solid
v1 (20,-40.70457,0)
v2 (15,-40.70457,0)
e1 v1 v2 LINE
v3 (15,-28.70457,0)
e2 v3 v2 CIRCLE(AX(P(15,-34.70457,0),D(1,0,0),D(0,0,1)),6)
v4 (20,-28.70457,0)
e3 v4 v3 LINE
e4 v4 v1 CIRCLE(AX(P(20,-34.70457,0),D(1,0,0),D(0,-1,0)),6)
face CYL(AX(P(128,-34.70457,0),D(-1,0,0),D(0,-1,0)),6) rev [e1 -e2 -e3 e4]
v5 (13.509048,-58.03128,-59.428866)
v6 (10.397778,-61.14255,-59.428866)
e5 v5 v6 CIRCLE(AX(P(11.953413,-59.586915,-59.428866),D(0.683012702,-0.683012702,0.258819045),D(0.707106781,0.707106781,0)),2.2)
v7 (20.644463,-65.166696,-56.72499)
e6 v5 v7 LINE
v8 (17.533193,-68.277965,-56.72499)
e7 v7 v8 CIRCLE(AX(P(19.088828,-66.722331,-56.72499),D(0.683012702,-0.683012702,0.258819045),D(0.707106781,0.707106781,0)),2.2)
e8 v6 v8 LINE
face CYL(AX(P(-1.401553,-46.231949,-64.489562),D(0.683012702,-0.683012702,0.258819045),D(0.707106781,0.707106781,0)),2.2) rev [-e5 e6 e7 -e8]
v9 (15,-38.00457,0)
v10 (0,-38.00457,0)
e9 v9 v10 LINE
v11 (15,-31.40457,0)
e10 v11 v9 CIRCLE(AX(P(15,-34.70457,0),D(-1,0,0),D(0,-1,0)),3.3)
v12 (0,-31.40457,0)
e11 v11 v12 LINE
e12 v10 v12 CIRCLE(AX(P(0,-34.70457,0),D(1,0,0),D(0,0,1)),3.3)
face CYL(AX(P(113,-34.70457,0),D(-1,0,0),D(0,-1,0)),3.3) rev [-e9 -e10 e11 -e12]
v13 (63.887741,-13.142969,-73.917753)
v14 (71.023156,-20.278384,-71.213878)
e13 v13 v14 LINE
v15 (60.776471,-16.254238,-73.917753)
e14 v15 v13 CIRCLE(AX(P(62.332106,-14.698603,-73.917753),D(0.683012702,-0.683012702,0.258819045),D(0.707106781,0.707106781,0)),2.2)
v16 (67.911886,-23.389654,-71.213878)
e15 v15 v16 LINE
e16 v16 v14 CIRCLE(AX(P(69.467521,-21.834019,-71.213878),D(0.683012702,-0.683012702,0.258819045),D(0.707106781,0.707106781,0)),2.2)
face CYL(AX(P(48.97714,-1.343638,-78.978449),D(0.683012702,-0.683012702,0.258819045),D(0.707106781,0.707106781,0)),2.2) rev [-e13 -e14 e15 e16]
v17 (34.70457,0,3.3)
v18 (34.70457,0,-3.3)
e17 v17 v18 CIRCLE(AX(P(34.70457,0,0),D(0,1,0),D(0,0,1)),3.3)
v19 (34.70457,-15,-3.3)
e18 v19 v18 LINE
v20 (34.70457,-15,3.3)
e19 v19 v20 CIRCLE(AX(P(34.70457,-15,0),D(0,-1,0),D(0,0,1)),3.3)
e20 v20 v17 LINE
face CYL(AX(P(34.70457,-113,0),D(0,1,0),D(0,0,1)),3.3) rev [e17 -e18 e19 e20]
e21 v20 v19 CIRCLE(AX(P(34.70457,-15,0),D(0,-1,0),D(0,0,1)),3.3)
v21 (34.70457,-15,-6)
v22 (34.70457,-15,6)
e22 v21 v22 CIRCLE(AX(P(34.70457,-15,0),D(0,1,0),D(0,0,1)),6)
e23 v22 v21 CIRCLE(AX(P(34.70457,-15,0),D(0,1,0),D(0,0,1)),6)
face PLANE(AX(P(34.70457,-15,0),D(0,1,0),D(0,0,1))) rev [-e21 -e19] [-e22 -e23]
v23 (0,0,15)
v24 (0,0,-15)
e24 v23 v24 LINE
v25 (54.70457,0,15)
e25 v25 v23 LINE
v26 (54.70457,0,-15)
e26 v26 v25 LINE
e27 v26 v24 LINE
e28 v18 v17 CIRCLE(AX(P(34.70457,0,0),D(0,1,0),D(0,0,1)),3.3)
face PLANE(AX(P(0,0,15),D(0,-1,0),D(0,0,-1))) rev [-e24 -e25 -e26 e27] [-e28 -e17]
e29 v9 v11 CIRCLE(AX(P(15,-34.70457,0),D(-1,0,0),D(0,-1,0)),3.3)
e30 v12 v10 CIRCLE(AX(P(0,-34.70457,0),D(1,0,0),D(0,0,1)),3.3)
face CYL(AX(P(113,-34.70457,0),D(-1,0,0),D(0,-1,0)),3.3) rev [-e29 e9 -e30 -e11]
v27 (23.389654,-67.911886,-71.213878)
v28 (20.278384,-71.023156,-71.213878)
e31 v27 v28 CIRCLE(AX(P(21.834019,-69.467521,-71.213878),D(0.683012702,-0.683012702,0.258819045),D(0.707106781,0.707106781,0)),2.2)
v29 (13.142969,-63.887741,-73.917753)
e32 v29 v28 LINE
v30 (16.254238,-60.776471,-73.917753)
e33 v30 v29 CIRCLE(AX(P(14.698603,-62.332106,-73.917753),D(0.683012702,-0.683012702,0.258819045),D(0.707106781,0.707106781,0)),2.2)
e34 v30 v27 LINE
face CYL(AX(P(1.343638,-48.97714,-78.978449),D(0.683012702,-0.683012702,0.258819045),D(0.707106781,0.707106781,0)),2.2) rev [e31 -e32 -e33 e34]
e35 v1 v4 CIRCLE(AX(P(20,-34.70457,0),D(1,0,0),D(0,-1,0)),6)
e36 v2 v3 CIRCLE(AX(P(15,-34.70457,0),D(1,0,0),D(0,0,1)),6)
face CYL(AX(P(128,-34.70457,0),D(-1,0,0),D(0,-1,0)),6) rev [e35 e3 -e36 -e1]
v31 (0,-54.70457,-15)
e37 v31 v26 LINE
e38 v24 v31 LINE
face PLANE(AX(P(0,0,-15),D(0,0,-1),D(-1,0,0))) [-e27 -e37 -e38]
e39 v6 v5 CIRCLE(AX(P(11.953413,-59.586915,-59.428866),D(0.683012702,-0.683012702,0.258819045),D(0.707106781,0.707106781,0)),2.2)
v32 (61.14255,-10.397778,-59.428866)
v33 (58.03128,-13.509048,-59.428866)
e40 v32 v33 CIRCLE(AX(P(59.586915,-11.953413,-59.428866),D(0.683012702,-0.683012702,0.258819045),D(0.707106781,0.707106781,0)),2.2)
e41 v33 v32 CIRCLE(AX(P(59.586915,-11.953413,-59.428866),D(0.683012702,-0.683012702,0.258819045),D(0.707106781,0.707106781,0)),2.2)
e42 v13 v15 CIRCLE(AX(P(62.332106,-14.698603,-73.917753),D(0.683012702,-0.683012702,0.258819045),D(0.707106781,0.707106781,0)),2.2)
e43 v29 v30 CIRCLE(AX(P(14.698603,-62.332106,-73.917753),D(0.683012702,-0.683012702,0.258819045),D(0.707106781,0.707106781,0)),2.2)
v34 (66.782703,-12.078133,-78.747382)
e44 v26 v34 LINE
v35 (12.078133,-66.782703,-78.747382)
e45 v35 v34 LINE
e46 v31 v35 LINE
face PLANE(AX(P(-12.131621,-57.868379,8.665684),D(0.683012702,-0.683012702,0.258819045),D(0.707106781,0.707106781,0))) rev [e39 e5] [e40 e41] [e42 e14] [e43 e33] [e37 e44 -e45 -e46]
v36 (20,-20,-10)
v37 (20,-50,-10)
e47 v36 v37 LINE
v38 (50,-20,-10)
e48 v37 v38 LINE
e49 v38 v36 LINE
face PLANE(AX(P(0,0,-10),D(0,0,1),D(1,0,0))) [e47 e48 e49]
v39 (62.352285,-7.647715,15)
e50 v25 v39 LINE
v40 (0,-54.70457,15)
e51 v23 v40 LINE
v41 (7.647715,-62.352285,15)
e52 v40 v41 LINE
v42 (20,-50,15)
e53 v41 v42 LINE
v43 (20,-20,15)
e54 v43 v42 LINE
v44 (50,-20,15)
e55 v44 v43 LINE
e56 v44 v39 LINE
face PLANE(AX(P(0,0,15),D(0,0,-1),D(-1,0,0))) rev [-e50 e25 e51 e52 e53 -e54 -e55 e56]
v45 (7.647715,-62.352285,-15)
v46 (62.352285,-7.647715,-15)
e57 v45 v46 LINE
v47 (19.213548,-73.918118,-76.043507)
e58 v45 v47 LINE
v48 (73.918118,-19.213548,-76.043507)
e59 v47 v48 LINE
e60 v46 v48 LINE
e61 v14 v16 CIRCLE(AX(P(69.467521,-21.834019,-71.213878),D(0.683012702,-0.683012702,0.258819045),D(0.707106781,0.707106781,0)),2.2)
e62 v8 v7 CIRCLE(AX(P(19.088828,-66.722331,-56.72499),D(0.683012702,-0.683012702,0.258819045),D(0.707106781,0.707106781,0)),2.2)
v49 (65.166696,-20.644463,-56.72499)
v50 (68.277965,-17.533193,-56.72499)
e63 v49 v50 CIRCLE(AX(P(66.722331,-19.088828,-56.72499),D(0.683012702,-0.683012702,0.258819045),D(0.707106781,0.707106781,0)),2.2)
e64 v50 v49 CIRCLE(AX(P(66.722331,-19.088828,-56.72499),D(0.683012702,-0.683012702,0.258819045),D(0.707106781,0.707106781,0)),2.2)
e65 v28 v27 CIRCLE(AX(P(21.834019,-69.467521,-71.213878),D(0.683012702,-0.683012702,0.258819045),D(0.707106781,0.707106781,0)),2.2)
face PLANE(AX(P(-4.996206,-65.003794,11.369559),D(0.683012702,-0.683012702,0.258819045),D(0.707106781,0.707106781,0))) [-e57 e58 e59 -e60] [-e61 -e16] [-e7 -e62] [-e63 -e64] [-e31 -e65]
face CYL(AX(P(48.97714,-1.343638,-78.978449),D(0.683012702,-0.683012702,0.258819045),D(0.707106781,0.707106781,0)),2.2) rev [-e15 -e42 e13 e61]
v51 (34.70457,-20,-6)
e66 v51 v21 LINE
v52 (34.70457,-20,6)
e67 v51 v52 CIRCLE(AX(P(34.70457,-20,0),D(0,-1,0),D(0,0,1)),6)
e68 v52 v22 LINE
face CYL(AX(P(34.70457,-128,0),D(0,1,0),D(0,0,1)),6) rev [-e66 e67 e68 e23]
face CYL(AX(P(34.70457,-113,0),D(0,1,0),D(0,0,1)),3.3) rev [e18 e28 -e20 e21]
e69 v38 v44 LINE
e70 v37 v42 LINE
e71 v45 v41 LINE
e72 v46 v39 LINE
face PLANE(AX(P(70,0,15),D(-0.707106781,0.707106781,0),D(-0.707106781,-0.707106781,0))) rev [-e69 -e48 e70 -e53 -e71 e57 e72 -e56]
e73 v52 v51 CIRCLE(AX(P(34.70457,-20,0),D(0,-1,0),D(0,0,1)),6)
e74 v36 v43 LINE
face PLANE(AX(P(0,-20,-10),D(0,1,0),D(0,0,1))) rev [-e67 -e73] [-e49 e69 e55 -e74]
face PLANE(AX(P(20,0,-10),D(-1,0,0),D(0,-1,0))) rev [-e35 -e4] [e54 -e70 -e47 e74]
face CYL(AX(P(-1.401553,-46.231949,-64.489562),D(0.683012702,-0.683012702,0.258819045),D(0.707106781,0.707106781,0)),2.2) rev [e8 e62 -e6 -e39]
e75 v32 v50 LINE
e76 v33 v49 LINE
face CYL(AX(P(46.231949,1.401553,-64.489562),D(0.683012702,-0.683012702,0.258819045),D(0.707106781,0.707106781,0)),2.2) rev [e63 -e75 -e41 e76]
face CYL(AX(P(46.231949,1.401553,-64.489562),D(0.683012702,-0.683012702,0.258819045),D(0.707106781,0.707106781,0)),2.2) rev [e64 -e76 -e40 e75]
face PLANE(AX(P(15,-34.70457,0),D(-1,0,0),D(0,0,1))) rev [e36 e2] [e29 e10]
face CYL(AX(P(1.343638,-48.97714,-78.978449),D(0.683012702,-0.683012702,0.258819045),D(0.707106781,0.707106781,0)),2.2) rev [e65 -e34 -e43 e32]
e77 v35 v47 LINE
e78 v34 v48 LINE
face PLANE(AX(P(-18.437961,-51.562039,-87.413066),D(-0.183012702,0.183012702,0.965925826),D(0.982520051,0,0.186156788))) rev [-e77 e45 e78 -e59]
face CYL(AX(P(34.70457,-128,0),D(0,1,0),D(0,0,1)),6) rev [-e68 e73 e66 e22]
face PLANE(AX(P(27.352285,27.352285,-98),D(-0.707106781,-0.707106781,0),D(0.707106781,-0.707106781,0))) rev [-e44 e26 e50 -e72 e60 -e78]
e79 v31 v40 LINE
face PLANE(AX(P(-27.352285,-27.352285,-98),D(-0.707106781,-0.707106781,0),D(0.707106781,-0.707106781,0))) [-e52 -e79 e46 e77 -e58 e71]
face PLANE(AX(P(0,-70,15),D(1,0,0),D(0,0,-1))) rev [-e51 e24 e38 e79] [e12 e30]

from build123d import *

# Parameters (mm, degrees)
EXTRUDE_1_DEPTH      = 15
EXTRUDE_2_DEPTH      = 49.497475
EXTRUDE_2_DEPTH_BACK = 49.497475
CUT_EXTRUDE_3_DEPTH  = 113
SKETCH_8_R           = 3.3
CUT_EXTRUDE_4_DEPTH  = 113
CUT_EXTRUDE_START    = -15
SKETCH_9_R           = 6
CUT_EXTRUDE_5_DEPTH  = 113
CUT_EXTRUDE_6_DEPTH  = 25
SKETCH_11_R          = 2.2
CUT_EXTRUDE_7_DEPTH  = 30


with BuildPart() as part:
    # 草图1 → 凸台-拉伸1 (new, symmetric)
    with BuildSketch(Plane.XY):
        Polygon((0, 0), (70, 0), (0, -70), align=None)
    extrude(amount=EXTRUDE_1_DEPTH, both=True)

    # 草图5 → 凸台-拉伸2 (add, two sides: drawn at the far end of the back side and taken through both)
    with BuildSketch(Plane(origin=(0, 0, 0), x_dir=(0.7071067811865476, -0.7071067811865476, 0), z_dir=(-0.7071067811865476, -0.7071067811865476, 0)).offset(-EXTRUDE_2_DEPTH_BACK)):
        Polygon((65.854033042, -76.043506833), (49.497474683, -15), (38.68197258, -15), (55.763032203, -78.747382359), align=None)
    extrude(amount=EXTRUDE_2_DEPTH + EXTRUDE_2_DEPTH_BACK)

    # 草图7 → 切除-拉伸3 (cut)
    with BuildSketch(Plane.XY.offset(15)):
        Polygon((70, 0), (54.704570242, 0), (62.352285121, -7.647714879), align=None)
        Polygon((62.352285121, 7.647714879), (54.704570242, 0), (70, 0), align=None)
        Polygon((70, 0), (62.352285121, -7.647714879), (73.918118454, -19.213548212), (81.565833333, -11.565833333), align=None)
        Polygon((19.213548212, -73.918118454), (7.647714879, -62.352285121), (0, -70), (11.565833333, -81.565833333), align=None)
        Polygon((0, -70), (7.647714879, -62.352285121), (0, -54.704570242), align=None)
        Polygon((0, -70), (0, -54.704570242), (-7.647714879, -62.352285121), align=None)
    extrude(amount=-CUT_EXTRUDE_3_DEPTH, mode=Mode.SUBTRACT)

    # 草图8 → 切除-拉伸4 (cut)
    with BuildSketch(Plane(origin=(0, 0, 0), x_dir=(1, 0, 0), z_dir=(0, 1, 0))):
        with Locations(Location((34.704570242, 0, 0), (0, 0, 270))):
            Circle(SKETCH_8_R)
    cut_extrude_4 = extrude(amount=-CUT_EXTRUDE_4_DEPTH, mode=Mode.SUBTRACT)

    # 草图9 → 切除-拉伸5 (cut)
    with BuildSketch(Plane(origin=(0, 0, 0), x_dir=(1, 0, 0), z_dir=(0, 1, 0)).offset(CUT_EXTRUDE_START)):
        with Locations(Location((34.704570242, 0, 0), (0, 0, 270))):
            Circle(SKETCH_9_R)
    cut_extrude_5 = extrude(amount=-CUT_EXTRUDE_5_DEPTH, mode=Mode.SUBTRACT)

    # 草图10 → 切除-拉伸6 (cut)
    with BuildSketch(Plane.XY.offset(15)):
        Polygon((20, -20), (20, -50), (47.352285121, -22.647714879), (50, -20), align=None)
    extrude(amount=-CUT_EXTRUDE_6_DEPTH, mode=Mode.SUBTRACT)

    # 镜向2: 切除-拉伸4, 切除-拉伸5 across plane
    add(cut_extrude_4.mirror(Plane(origin=(0, 0, 0), x_dir=(0, 0, 1), z_dir=(-0.7071067811865476, -0.7071067811865476, 0))), mode=Mode.SUBTRACT)
    add(cut_extrude_5.mirror(Plane(origin=(0, 0, 0), x_dir=(0, 0, 1), z_dir=(-0.7071067811865476, -0.7071067811865476, 0))), mode=Mode.SUBTRACT)

    # 草图11 → 切除-拉伸7 (cut)
    with BuildSketch(Plane(origin=(30.003794137, -30.003794137, 11.369559199), x_dir=(0.18301270189221028, -0.18301270189221025, -0.9659258262890718), z_dir=(0.6830127018922219, -0.6830127018922217, 0.25881904510250797))):
        with Locations(Location((70.49666512, 33.68197258, 0), (0, 0, 90))):
            Circle(SKETCH_11_R)
        with Locations(Location((85.49666512, 33.68197258, 0), (0, 0, 90))):
            Circle(SKETCH_11_R)
        with Locations(Location((85.49666512, -33.68197258, 0), (0, 0, 90))):
            Circle(SKETCH_11_R)
        with Locations(Location((70.49666512, -33.68197258, 0), (0, 0, 90))):
            Circle(SKETCH_11_R)
    extrude(amount=-CUT_EXTRUDE_7_DEPTH, mode=Mode.SUBTRACT)


solid = part.part
